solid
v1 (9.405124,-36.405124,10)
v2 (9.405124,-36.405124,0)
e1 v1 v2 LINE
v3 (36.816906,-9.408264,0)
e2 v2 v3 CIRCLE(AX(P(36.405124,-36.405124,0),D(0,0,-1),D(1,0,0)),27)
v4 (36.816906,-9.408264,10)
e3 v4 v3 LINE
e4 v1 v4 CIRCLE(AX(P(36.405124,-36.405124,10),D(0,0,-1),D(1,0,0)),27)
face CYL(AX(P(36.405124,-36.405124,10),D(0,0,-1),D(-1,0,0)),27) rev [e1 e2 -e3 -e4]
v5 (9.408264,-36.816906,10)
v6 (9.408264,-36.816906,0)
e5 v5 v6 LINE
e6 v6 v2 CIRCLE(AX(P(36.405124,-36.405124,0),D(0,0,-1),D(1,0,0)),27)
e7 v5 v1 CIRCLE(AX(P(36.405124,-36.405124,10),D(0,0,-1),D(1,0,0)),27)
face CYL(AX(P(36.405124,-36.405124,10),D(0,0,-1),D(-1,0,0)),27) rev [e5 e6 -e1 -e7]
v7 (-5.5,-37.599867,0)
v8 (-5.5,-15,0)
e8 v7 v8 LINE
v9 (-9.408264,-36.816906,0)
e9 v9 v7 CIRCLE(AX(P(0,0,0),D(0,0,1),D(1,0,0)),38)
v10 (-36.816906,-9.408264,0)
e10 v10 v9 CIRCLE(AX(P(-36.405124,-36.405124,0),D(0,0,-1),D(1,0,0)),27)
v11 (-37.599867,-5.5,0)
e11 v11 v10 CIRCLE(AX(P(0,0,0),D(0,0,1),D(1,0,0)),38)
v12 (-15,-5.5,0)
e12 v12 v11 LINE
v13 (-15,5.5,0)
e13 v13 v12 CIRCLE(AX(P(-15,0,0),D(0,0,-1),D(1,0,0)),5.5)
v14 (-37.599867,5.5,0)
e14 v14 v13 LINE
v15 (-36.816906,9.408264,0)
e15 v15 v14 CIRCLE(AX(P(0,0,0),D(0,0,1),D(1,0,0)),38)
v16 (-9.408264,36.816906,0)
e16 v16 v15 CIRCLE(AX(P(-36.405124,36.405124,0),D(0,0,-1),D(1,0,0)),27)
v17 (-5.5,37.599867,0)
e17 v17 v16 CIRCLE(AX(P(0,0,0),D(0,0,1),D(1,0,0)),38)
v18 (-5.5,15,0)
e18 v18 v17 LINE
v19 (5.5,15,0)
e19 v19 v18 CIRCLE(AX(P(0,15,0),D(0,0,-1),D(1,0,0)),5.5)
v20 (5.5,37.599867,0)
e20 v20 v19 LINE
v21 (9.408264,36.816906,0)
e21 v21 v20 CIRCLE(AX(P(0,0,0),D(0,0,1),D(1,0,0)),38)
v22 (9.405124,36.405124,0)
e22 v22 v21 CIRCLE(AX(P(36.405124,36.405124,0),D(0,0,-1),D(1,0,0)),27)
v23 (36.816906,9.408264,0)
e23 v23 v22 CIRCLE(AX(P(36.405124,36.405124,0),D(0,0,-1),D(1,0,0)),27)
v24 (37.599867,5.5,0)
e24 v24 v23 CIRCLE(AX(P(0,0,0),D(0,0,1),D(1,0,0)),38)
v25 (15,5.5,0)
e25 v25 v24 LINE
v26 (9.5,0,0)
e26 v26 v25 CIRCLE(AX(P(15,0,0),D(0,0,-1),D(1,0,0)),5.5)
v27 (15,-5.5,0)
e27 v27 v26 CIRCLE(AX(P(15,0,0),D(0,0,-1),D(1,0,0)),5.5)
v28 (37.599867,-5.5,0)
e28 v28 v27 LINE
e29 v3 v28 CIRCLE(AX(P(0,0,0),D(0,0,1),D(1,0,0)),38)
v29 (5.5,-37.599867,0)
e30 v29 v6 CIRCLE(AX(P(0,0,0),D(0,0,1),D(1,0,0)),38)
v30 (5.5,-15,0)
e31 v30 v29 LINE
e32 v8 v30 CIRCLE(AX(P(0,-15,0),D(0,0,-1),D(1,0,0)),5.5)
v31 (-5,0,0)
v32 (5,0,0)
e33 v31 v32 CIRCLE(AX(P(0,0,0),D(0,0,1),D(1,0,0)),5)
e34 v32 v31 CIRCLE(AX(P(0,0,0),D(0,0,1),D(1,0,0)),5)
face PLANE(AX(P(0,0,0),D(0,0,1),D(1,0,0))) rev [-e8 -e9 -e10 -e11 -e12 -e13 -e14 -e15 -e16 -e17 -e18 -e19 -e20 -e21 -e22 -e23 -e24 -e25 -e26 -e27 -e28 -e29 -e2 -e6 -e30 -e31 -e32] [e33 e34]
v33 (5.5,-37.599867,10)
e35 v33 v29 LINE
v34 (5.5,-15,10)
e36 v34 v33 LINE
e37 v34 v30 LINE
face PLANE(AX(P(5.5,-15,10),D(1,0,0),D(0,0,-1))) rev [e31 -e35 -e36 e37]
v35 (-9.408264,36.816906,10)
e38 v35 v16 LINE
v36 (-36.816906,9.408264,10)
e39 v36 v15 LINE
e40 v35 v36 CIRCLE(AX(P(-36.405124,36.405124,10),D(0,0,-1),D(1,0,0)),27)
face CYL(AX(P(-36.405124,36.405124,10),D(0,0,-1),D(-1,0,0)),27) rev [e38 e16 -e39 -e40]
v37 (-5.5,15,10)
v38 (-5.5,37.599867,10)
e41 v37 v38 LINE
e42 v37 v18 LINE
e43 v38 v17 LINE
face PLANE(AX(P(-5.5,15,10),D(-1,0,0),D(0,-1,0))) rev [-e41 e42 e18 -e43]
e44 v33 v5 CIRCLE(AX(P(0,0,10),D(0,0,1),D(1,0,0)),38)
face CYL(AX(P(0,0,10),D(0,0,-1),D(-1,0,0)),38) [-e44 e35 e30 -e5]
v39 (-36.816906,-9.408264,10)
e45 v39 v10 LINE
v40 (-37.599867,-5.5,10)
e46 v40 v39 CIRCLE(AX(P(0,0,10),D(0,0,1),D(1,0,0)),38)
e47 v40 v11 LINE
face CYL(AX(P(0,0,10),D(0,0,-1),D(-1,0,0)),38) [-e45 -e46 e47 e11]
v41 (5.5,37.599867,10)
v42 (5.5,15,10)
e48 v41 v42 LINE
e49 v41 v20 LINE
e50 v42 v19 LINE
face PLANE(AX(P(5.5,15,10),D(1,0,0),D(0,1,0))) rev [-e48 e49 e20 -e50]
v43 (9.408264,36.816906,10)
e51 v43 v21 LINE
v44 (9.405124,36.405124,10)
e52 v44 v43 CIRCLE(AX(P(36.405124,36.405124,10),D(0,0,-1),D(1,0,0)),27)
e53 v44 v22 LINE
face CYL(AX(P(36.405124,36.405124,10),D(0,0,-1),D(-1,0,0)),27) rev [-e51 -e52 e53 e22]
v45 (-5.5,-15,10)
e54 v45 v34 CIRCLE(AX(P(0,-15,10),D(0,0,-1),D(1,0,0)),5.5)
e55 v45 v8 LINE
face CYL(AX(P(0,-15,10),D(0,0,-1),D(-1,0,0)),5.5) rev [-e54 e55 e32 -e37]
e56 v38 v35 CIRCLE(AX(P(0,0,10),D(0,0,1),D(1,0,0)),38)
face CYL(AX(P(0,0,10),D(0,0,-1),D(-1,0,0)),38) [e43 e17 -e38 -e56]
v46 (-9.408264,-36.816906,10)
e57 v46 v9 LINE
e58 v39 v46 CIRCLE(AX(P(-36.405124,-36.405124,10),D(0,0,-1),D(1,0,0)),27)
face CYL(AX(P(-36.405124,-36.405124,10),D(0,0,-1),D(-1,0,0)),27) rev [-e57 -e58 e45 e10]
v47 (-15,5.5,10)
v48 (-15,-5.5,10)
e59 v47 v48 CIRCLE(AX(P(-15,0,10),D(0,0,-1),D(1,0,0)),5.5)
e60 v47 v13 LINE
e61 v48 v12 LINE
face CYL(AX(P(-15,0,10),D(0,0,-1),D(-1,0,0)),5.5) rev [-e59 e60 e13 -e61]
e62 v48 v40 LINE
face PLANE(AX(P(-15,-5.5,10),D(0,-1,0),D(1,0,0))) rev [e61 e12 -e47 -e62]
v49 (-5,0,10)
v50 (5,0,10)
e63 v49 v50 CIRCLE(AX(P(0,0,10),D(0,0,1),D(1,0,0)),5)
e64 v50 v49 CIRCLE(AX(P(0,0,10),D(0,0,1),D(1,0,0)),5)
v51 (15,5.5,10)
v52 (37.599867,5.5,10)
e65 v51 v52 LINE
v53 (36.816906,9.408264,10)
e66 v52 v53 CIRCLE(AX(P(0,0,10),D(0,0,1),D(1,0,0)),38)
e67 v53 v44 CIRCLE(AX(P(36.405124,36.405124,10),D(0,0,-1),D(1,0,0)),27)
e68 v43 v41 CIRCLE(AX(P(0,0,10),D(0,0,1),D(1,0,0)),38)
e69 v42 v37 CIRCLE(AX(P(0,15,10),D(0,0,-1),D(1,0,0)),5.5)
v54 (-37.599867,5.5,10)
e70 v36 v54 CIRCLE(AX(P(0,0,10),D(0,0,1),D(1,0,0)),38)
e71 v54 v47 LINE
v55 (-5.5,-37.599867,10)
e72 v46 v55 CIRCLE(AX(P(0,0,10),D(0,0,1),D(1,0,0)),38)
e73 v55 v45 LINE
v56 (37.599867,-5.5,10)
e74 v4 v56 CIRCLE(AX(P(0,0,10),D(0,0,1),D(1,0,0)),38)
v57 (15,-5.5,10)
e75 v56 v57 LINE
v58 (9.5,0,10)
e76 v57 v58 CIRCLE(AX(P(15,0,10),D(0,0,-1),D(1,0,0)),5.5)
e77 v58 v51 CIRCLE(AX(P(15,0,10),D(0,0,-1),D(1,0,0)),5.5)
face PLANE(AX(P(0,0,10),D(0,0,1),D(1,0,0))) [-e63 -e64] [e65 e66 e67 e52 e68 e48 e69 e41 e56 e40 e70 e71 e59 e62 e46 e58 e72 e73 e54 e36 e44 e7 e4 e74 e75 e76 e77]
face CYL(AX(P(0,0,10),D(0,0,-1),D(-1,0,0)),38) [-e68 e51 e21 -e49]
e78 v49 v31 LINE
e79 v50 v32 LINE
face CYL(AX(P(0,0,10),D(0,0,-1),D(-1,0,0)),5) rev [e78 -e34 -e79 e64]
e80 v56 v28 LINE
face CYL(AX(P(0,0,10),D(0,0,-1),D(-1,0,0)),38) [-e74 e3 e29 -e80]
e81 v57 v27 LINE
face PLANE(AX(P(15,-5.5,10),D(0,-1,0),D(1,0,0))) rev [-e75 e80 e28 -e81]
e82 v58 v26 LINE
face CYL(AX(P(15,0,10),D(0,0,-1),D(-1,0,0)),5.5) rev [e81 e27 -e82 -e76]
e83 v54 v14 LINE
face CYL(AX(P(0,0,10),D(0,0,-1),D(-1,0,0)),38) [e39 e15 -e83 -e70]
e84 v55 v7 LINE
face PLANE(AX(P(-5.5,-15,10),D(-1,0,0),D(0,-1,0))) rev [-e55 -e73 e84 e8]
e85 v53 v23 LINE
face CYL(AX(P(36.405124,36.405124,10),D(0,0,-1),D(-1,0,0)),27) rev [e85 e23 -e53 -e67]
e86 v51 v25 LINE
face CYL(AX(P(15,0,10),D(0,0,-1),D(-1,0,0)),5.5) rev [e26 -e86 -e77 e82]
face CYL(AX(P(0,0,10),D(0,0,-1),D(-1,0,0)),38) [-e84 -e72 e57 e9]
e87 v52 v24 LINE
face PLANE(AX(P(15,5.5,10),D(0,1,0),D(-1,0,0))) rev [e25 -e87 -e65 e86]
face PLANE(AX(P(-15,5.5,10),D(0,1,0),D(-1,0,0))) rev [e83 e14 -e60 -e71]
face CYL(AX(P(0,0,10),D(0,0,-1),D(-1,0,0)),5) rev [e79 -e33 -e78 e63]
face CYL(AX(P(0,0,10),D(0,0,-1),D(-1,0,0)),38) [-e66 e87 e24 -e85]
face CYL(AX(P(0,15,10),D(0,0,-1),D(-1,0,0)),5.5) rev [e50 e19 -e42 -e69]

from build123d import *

# Parameters (mm, degrees)
SPIDER_PLATE_PROFILE_R          = 5
SPIDER_PLATE_EXTRUDE_10MM_DEPTH = 10


with BuildPart() as part:
    # Spider Plate Profile → Spider Plate Extrude 10mm (new body)
    with BuildSketch(Plane.XY):
        with BuildLine():
            Line((5.5, -15), (5.5, -37.599867021))
            ThreePointArc((5.5, -37.599867021), (7.46440512, -37.259665272), (9.408264389, -36.816905916))
            ThreePointArc((9.408264389, -36.816905916), (17.313241035, -17.313241035), (36.816905916, -9.408264389))
            ThreePointArc((36.816905916, -9.408264389), (37.259665272, -7.46440512), (37.599867021, -5.5))
            Line((37.599867021, -5.5), (15, -5.5))
            ThreePointArc((15, -5.5), (9.5, 0), (15, 5.5))
            Line((15, 5.5), (37.599867021, 5.5))
            ThreePointArc((37.599867021, 5.5), (37.259665272, 7.46440512), (36.816905916, 9.408264389))
            ThreePointArc((36.816905916, 9.408264389), (17.313241035, 17.313241035), (9.408264389, 36.816905916))
            ThreePointArc((9.408264389, 36.816905916), (7.46440512, 37.259665272), (5.5, 37.599867021))
            Line((5.5, 37.599867021), (5.5, 15))
            ThreePointArc((5.5, 15), (0, 9.5), (-5.5, 15))
            Line((-5.5, 15), (-5.5, 37.599867021))
            ThreePointArc((-5.5, 37.599867021), (-7.46440512, 37.259665272), (-9.408264389, 36.816905916))
            ThreePointArc((-9.408264389, 36.816905916), (-17.313241035, 17.313241035), (-36.816905916, 9.408264389))
            ThreePointArc((-36.816905916, 9.408264389), (-37.259665272, 7.46440512), (-37.599867021, 5.5))
            Line((-37.599867021, 5.5), (-15, 5.5))
            ThreePointArc((-15, 5.5), (-9.5, 0), (-15, -5.5))
            Line((-15, -5.5), (-37.599867021, -5.5))
            ThreePointArc((-37.599867021, -5.5), (-37.259665272, -7.46440512), (-36.816905916, -9.408264389))
            ThreePointArc((-36.816905916, -9.408264389), (-17.313241035, -17.313241035), (-9.408264389, -36.816905916))
            ThreePointArc((-9.408264389, -36.816905916), (-7.46440512, -37.259665272), (-5.5, -37.599867021))
            Line((-5.5, -37.599867021), (-5.5, -15))
            ThreePointArc((-5.5, -15), (0, -9.5), (5.5, -15))
        make_face()
        Circle(SPIDER_PLATE_PROFILE_R, mode=Mode.SUBTRACT)
    extrude(amount=SPIDER_PLATE_EXTRUDE_10MM_DEPTH)


solid = part.part
